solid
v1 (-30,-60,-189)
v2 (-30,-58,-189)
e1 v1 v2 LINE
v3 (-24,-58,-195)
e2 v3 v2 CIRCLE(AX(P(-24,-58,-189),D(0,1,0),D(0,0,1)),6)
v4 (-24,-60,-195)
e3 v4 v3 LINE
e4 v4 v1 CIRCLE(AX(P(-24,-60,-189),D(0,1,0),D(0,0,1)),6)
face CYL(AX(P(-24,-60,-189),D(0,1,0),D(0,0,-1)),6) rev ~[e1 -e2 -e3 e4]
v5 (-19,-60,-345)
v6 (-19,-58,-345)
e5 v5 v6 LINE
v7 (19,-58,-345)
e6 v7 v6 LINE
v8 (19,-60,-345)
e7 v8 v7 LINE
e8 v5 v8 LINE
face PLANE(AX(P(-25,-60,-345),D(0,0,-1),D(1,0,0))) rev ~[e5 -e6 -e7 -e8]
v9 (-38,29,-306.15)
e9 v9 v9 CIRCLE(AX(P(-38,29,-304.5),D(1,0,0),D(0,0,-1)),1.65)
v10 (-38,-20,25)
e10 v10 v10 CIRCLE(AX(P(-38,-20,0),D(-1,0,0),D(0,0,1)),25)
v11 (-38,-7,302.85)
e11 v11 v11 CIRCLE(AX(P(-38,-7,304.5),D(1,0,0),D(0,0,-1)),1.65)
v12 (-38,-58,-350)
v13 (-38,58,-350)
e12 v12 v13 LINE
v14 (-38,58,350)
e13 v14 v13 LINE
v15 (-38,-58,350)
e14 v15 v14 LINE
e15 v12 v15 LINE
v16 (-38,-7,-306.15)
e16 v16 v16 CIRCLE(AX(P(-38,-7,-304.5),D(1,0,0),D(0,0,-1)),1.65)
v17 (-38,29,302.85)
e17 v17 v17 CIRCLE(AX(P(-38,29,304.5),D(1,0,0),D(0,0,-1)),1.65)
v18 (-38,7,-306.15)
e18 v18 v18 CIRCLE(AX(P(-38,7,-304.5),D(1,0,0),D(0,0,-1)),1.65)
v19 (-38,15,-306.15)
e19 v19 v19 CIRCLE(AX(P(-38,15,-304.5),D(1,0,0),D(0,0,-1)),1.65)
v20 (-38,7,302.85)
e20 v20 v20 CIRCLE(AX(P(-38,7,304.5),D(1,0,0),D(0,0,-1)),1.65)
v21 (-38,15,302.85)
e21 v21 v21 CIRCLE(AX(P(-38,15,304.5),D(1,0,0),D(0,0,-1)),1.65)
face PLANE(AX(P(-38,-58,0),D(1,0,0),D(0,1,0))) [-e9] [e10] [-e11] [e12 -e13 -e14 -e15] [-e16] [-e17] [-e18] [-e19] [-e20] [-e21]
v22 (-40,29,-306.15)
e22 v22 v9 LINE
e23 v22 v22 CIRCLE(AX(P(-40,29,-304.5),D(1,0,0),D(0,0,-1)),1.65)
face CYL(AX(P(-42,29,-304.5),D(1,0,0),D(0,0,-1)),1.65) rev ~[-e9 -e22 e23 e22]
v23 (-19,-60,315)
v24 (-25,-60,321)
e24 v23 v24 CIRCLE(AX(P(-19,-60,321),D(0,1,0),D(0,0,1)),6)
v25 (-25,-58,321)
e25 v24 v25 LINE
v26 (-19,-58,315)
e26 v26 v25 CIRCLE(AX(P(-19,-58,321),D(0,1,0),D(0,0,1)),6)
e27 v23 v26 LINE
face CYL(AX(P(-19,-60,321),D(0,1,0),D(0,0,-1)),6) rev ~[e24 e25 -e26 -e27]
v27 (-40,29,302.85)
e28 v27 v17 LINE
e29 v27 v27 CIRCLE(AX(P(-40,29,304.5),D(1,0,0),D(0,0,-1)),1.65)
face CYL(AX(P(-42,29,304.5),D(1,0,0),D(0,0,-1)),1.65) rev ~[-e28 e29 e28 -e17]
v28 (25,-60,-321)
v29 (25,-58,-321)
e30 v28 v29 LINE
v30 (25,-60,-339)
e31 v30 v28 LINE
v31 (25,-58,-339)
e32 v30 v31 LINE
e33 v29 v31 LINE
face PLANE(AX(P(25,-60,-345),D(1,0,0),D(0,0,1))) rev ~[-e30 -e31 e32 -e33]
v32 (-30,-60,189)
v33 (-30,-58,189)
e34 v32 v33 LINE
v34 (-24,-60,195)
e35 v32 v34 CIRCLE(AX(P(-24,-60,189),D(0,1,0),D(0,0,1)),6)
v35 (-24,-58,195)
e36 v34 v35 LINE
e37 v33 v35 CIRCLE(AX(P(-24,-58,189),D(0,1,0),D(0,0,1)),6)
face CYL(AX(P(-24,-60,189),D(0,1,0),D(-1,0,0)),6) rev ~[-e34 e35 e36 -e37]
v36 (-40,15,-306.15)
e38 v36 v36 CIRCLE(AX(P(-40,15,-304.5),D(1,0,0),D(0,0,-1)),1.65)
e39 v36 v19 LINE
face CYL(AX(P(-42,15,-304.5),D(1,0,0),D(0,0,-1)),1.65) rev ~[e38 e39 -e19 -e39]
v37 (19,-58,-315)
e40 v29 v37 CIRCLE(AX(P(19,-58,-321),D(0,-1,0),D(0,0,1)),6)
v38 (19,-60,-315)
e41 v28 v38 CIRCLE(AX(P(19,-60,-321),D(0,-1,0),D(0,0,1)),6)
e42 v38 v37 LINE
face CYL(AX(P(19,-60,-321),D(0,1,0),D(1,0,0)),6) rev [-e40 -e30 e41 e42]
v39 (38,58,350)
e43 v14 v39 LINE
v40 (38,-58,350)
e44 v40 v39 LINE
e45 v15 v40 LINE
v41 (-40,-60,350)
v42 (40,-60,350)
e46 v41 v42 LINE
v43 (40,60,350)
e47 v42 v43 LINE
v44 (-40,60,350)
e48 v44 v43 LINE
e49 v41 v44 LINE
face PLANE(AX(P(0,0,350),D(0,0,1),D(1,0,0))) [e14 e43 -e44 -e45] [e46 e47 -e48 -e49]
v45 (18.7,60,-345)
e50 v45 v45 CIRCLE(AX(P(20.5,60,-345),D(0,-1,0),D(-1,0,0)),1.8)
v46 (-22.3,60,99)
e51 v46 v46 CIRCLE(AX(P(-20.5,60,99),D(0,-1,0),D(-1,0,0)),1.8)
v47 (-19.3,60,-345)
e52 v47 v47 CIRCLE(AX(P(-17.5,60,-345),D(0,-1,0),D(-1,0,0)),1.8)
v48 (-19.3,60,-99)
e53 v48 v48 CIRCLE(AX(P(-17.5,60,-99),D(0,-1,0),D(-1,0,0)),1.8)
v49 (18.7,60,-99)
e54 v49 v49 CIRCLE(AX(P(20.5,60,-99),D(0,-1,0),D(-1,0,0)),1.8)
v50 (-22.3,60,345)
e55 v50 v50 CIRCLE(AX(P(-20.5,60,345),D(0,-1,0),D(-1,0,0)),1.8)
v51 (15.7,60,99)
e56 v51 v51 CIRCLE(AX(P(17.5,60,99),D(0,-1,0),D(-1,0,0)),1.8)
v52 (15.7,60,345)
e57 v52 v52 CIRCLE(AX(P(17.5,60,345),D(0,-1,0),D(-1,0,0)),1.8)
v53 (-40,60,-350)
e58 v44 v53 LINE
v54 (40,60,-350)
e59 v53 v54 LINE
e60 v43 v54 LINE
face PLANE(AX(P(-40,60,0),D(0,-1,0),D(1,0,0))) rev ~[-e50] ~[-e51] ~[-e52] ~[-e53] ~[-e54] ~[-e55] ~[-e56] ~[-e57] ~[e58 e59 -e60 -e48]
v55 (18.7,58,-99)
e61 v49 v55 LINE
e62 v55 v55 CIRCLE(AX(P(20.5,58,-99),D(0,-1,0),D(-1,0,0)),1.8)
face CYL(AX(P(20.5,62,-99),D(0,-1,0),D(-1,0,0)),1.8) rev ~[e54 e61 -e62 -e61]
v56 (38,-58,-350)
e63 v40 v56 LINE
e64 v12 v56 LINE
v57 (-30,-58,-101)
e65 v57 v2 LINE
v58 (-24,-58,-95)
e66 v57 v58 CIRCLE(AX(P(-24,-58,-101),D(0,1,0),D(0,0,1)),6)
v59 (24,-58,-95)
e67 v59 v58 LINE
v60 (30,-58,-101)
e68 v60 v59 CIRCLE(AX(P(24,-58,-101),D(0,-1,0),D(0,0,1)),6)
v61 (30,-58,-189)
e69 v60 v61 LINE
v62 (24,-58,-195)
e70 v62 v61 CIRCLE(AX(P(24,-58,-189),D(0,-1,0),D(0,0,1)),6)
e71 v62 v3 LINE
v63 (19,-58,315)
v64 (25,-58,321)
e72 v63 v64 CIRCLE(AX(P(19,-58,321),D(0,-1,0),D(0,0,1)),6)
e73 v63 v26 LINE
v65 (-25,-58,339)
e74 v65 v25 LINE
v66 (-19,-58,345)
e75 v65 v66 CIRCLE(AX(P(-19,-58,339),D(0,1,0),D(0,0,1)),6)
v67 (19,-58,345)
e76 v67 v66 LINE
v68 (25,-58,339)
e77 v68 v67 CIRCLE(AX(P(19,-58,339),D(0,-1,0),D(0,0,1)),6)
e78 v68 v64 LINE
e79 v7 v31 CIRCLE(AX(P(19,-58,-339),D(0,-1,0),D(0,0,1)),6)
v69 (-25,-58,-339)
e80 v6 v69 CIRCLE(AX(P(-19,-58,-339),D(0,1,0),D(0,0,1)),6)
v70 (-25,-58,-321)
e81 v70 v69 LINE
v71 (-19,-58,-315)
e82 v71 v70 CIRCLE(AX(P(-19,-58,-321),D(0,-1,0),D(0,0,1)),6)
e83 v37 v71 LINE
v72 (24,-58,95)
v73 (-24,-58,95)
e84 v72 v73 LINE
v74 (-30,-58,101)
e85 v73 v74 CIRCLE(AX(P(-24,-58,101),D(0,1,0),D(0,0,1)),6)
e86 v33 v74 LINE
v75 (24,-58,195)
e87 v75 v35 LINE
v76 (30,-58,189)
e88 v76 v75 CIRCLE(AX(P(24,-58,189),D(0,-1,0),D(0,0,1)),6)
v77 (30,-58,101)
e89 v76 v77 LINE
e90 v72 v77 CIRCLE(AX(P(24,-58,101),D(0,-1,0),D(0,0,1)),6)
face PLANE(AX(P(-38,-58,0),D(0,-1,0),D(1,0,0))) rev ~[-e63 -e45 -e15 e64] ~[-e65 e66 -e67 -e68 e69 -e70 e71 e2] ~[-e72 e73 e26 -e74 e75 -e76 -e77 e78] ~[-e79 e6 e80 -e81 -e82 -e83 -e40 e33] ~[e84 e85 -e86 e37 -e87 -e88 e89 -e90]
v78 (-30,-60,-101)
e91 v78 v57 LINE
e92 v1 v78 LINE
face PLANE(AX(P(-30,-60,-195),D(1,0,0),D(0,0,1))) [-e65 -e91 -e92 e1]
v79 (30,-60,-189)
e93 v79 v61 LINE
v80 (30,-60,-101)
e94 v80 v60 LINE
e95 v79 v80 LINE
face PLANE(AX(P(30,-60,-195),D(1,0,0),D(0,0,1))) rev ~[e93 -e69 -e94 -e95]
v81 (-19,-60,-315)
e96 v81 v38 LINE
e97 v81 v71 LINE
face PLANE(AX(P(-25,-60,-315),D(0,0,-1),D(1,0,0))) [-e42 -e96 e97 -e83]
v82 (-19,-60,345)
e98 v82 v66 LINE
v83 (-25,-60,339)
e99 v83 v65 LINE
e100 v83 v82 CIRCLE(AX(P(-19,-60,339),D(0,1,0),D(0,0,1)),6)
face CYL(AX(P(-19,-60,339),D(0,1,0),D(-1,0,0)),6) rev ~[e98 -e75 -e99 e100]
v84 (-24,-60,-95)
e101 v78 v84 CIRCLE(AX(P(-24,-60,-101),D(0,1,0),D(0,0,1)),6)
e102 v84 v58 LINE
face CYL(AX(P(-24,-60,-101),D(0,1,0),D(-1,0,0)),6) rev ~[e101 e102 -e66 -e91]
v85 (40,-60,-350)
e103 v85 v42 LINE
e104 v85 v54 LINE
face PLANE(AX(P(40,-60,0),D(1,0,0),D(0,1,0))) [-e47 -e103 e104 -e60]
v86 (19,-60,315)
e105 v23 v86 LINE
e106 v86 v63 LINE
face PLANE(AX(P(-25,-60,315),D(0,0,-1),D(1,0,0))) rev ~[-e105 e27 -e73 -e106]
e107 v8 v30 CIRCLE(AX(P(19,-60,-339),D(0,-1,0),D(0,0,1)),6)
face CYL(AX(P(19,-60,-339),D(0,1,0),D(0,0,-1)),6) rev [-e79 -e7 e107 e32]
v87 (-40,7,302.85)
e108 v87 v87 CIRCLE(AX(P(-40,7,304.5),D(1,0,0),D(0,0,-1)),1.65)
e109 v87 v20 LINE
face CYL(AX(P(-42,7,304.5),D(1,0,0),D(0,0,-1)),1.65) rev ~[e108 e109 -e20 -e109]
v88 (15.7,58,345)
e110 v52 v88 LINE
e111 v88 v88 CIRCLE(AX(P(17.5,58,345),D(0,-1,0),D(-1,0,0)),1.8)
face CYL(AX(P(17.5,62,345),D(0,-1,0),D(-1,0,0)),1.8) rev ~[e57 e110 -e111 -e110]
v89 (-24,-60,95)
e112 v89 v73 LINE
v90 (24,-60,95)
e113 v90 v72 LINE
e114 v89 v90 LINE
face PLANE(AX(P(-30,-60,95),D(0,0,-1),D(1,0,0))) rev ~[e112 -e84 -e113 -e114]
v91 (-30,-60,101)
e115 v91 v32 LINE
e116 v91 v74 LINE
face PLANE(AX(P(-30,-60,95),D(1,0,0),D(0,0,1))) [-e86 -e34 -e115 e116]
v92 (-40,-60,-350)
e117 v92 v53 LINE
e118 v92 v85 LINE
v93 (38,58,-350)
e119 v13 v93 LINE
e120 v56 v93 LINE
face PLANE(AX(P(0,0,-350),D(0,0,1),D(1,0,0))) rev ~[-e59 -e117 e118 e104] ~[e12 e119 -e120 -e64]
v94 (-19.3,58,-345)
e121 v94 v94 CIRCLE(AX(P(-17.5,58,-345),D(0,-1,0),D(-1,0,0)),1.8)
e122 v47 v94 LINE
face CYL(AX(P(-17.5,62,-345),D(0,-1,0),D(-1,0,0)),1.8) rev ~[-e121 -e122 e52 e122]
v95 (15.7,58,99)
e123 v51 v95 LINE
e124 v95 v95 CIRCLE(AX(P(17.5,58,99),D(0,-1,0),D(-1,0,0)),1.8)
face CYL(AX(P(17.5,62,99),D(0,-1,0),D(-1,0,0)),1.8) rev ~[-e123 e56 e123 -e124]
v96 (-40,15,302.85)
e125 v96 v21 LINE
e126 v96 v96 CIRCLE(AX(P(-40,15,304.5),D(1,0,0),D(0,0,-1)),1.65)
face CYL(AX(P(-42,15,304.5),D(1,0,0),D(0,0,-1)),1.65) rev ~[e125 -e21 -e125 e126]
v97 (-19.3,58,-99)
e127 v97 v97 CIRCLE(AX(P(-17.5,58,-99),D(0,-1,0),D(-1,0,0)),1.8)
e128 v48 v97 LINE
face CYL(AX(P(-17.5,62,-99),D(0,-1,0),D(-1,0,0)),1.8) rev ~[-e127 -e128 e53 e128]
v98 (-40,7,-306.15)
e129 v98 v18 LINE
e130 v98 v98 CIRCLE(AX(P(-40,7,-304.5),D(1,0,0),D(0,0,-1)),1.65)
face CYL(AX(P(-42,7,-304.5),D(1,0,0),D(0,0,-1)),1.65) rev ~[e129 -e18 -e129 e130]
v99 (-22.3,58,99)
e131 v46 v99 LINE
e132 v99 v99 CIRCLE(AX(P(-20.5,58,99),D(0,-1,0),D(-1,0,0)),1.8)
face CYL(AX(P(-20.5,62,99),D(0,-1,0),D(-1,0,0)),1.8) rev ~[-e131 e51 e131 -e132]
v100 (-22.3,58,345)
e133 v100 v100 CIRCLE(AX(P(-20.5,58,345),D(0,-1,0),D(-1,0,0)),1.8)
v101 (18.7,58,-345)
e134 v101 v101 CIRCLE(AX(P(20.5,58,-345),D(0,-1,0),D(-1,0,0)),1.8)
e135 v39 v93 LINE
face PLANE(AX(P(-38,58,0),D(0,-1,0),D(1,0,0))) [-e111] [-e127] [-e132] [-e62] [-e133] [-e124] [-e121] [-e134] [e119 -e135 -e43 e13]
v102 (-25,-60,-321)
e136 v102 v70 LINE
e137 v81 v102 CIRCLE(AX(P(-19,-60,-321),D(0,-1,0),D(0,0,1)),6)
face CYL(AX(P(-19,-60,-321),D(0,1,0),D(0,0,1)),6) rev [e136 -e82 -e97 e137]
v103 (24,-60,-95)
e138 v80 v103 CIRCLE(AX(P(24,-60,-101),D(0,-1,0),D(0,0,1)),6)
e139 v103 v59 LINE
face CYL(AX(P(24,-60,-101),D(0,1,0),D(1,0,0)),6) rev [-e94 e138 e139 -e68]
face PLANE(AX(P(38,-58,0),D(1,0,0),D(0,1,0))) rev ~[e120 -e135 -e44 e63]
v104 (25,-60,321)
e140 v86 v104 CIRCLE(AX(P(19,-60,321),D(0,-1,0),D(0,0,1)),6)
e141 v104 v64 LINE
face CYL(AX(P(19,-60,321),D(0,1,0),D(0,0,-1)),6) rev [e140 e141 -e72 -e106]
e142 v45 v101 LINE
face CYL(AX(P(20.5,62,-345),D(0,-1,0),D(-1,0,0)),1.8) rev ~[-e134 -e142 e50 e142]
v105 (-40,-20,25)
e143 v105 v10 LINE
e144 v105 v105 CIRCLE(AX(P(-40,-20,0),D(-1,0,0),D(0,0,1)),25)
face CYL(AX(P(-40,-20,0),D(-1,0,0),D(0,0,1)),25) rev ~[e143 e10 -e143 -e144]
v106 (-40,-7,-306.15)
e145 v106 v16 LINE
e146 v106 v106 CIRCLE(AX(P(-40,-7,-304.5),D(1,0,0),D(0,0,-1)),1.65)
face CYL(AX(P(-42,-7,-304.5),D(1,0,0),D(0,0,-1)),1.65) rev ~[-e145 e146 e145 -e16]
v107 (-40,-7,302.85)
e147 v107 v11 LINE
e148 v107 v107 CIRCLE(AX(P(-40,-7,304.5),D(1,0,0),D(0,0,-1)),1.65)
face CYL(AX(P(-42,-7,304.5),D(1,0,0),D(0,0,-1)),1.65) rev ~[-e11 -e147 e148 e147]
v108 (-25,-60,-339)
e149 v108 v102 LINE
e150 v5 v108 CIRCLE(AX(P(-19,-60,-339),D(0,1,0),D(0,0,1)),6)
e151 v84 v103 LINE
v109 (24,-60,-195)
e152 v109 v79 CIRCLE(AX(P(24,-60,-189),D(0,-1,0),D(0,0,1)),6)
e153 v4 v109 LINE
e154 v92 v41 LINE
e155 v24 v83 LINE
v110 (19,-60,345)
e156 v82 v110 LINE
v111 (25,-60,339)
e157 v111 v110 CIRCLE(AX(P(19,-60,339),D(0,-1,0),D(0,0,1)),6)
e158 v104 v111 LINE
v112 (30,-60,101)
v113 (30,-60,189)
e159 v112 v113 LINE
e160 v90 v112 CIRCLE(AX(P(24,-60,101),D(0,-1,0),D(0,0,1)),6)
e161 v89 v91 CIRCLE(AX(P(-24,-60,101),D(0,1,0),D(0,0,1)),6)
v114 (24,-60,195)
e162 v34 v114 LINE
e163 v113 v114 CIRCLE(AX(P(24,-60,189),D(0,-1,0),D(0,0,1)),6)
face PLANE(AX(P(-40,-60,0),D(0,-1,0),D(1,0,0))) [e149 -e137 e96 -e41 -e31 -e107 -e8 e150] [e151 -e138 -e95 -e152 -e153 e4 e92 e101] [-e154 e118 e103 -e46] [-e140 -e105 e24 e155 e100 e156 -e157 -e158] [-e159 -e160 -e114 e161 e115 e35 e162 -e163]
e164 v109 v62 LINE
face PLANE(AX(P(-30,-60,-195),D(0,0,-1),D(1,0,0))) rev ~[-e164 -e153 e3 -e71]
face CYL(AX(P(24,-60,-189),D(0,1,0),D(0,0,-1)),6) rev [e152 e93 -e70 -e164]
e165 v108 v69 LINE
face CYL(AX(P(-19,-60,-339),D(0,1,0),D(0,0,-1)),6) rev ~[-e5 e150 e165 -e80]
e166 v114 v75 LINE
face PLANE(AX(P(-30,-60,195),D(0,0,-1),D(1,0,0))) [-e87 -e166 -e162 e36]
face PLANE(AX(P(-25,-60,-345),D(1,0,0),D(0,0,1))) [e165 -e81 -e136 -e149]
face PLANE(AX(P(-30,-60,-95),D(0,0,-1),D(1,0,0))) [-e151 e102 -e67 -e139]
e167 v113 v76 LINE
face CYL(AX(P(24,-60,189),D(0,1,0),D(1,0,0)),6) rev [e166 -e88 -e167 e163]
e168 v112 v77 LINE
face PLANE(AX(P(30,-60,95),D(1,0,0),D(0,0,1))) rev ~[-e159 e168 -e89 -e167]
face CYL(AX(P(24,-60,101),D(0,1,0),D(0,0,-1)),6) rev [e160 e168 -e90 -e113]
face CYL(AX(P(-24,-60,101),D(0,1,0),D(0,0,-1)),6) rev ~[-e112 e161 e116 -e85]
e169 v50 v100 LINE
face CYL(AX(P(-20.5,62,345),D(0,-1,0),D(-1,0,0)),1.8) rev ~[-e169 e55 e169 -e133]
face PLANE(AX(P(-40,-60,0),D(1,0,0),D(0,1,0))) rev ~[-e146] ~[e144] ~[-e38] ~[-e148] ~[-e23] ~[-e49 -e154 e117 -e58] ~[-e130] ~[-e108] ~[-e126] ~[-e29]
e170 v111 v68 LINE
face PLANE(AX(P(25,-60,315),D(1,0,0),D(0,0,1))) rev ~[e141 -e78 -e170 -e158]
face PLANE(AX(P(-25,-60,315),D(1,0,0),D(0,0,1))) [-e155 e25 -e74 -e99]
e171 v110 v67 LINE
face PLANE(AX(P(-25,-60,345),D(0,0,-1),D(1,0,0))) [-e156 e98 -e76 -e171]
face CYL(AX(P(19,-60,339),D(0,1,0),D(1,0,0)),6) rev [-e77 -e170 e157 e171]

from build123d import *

# Parameters (mm, degrees)
SKETCH_1_W             = 80
SKETCH_1_H             = 120
SKETCH_1_W_2           = 76
SKETCH_1_H_2           = 116
EXTRUDE_1_DEPTH        = 350
CUT_EXTRUDE_2_REACH    = 366.005
SKETCH_4_R             = 25
HOLE_WIZARD_M4_1_D     = 3.3
HOLE_WIZARD_M4_1_DEPTH = 2
HOLE_WIZARD_M3_1_D     = 3.6
HOLE_WIZARD_M3_1_DEPTH = 2
CUT_EXTRUDE_3_REACH    = 374.156
SKETCH_16_W            = 50
SKETCH_16_H            = 30
SKETCH_16_W_2          = 60
SKETCH_16_H_2          = 100
FILLET_1_R             = 6


with BuildPart() as part:
    # 草图1 → 拉伸-薄壁1 (new, symmetric)
    with BuildSketch(Plane.XY):
        Rectangle(SKETCH_1_W, SKETCH_1_H)
        Rectangle(SKETCH_1_W_2, SKETCH_1_H_2, mode=Mode.SUBTRACT)
    extrude(amount=EXTRUDE_1_DEPTH, both=True)

    # 草图4 → 切除-拉伸2 (cut, up to next)
    with BuildSketch(Plane.ZY.offset(40), mode=Mode.PRIVATE) as cut_extrude_2_sk1:
        with Locations((0, -20)):
            Circle(SKETCH_4_R)
    cut_extrude_2_tool1 = extrude(cut_extrude_2_sk1.sketch, amount=-CUT_EXTRUDE_2_REACH, mode=Mode.PRIVATE) & part.part
    add(cut_extrude_2_tool1.solids().sort_by_distance((-40, -20, 0))[0], mode=Mode.SUBTRACT)

    # Hole Wizard M4 _1
    with Locations(Plane.ZY.offset(40)):
        with Locations((304.5, 29), (304.5, 15), (304.5, 7), (304.5, -7), (-304.5, -7), (-304.5, 7), (-304.5, 15), (-304.5, 29)):
            Hole(HOLE_WIZARD_M4_1_D / 2, depth=HOLE_WIZARD_M4_1_DEPTH)

    # M3 间隙孔1
    with Locations(Plane(origin=(0, 60, 0), x_dir=(1, 0, 0), z_dir=(0, 1, 0))):
        with Locations((-17.5, 345), (20.5, 345), (20.5, 99), (-17.5, 99), (-20.5, -345), (17.5, -345), (-20.5, -99), (17.5, -99)):
            Hole(HOLE_WIZARD_M3_1_D / 2, depth=HOLE_WIZARD_M3_1_DEPTH)

    # 草图16 → 切除-拉伸3 (cut, up to next)
    with BuildSketch(Plane.XZ.offset(60), mode=Mode.PRIVATE) as cut_extrude_3_sk1:
        with Locations((0, 330)):
            Rectangle(SKETCH_16_W, SKETCH_16_H)
    cut_extrude_3_tool1 = extrude(cut_extrude_3_sk1.sketch, amount=-CUT_EXTRUDE_3_REACH, mode=Mode.PRIVATE) & part.part
    # 草图16 → 切除-拉伸3 (cut, up to next)
    with BuildSketch(Plane.XZ.offset(60), mode=Mode.PRIVATE) as cut_extrude_3_sk2:
        with Locations((0, 145)):
            Rectangle(SKETCH_16_W_2, SKETCH_16_H_2)
    cut_extrude_3_tool2 = extrude(cut_extrude_3_sk2.sketch, amount=-CUT_EXTRUDE_3_REACH, mode=Mode.PRIVATE) & part.part
    # 草图16 → 切除-拉伸3 (cut, up to next)
    with BuildSketch(Plane.XZ.offset(60), mode=Mode.PRIVATE) as cut_extrude_3_sk3:
        with Locations((0, -145)):
            Rectangle(SKETCH_16_W_2, SKETCH_16_H_2)
    cut_extrude_3_tool3 = extrude(cut_extrude_3_sk3.sketch, amount=-CUT_EXTRUDE_3_REACH, mode=Mode.PRIVATE) & part.part
    # 草图16 → 切除-拉伸3 (cut, up to next)
    with BuildSketch(Plane.XZ.offset(60), mode=Mode.PRIVATE) as cut_extrude_3_sk4:
        with Locations((0, -330)):
            Rectangle(SKETCH_16_W, SKETCH_16_H)
    cut_extrude_3_tool4 = extrude(cut_extrude_3_sk4.sketch, amount=-CUT_EXTRUDE_3_REACH, mode=Mode.PRIVATE) & part.part
    add(cut_extrude_3_tool1.solids().sort_by_distance((0, -60, 330))[0], mode=Mode.SUBTRACT)
    add(cut_extrude_3_tool2.solids().sort_by_distance((0, -60, 145))[0], mode=Mode.SUBTRACT)
    add(cut_extrude_3_tool3.solids().sort_by_distance((0, -60, -145))[0], mode=Mode.SUBTRACT)
    add(cut_extrude_3_tool4.solids().sort_by_distance((0, -60, -330))[0], mode=Mode.SUBTRACT)

    # 圆角1
    fillet_1_edges = [part.edges().sort_by_distance(p)[0] for p in [
        (25, -59, 315),
        (25, -59, 345),
        (-25, -59, 345),
        (-25, -59, 315),
        (30, -59, 95),
        (30, -59, 195),
        (-30, -59, 195),
        (-30, -59, 95),
        (30, -59, -95),
        (-30, -59, -95),
        (-30, -59, -195),
        (30, -59, -195),
        (25, -59, -315),
        (-25, -59, -315),
        (-25, -59, -345),
        (25, -59, -345),
    ]]
    fillet(fillet_1_edges, radius=FILLET_1_R)


solid = part.part
